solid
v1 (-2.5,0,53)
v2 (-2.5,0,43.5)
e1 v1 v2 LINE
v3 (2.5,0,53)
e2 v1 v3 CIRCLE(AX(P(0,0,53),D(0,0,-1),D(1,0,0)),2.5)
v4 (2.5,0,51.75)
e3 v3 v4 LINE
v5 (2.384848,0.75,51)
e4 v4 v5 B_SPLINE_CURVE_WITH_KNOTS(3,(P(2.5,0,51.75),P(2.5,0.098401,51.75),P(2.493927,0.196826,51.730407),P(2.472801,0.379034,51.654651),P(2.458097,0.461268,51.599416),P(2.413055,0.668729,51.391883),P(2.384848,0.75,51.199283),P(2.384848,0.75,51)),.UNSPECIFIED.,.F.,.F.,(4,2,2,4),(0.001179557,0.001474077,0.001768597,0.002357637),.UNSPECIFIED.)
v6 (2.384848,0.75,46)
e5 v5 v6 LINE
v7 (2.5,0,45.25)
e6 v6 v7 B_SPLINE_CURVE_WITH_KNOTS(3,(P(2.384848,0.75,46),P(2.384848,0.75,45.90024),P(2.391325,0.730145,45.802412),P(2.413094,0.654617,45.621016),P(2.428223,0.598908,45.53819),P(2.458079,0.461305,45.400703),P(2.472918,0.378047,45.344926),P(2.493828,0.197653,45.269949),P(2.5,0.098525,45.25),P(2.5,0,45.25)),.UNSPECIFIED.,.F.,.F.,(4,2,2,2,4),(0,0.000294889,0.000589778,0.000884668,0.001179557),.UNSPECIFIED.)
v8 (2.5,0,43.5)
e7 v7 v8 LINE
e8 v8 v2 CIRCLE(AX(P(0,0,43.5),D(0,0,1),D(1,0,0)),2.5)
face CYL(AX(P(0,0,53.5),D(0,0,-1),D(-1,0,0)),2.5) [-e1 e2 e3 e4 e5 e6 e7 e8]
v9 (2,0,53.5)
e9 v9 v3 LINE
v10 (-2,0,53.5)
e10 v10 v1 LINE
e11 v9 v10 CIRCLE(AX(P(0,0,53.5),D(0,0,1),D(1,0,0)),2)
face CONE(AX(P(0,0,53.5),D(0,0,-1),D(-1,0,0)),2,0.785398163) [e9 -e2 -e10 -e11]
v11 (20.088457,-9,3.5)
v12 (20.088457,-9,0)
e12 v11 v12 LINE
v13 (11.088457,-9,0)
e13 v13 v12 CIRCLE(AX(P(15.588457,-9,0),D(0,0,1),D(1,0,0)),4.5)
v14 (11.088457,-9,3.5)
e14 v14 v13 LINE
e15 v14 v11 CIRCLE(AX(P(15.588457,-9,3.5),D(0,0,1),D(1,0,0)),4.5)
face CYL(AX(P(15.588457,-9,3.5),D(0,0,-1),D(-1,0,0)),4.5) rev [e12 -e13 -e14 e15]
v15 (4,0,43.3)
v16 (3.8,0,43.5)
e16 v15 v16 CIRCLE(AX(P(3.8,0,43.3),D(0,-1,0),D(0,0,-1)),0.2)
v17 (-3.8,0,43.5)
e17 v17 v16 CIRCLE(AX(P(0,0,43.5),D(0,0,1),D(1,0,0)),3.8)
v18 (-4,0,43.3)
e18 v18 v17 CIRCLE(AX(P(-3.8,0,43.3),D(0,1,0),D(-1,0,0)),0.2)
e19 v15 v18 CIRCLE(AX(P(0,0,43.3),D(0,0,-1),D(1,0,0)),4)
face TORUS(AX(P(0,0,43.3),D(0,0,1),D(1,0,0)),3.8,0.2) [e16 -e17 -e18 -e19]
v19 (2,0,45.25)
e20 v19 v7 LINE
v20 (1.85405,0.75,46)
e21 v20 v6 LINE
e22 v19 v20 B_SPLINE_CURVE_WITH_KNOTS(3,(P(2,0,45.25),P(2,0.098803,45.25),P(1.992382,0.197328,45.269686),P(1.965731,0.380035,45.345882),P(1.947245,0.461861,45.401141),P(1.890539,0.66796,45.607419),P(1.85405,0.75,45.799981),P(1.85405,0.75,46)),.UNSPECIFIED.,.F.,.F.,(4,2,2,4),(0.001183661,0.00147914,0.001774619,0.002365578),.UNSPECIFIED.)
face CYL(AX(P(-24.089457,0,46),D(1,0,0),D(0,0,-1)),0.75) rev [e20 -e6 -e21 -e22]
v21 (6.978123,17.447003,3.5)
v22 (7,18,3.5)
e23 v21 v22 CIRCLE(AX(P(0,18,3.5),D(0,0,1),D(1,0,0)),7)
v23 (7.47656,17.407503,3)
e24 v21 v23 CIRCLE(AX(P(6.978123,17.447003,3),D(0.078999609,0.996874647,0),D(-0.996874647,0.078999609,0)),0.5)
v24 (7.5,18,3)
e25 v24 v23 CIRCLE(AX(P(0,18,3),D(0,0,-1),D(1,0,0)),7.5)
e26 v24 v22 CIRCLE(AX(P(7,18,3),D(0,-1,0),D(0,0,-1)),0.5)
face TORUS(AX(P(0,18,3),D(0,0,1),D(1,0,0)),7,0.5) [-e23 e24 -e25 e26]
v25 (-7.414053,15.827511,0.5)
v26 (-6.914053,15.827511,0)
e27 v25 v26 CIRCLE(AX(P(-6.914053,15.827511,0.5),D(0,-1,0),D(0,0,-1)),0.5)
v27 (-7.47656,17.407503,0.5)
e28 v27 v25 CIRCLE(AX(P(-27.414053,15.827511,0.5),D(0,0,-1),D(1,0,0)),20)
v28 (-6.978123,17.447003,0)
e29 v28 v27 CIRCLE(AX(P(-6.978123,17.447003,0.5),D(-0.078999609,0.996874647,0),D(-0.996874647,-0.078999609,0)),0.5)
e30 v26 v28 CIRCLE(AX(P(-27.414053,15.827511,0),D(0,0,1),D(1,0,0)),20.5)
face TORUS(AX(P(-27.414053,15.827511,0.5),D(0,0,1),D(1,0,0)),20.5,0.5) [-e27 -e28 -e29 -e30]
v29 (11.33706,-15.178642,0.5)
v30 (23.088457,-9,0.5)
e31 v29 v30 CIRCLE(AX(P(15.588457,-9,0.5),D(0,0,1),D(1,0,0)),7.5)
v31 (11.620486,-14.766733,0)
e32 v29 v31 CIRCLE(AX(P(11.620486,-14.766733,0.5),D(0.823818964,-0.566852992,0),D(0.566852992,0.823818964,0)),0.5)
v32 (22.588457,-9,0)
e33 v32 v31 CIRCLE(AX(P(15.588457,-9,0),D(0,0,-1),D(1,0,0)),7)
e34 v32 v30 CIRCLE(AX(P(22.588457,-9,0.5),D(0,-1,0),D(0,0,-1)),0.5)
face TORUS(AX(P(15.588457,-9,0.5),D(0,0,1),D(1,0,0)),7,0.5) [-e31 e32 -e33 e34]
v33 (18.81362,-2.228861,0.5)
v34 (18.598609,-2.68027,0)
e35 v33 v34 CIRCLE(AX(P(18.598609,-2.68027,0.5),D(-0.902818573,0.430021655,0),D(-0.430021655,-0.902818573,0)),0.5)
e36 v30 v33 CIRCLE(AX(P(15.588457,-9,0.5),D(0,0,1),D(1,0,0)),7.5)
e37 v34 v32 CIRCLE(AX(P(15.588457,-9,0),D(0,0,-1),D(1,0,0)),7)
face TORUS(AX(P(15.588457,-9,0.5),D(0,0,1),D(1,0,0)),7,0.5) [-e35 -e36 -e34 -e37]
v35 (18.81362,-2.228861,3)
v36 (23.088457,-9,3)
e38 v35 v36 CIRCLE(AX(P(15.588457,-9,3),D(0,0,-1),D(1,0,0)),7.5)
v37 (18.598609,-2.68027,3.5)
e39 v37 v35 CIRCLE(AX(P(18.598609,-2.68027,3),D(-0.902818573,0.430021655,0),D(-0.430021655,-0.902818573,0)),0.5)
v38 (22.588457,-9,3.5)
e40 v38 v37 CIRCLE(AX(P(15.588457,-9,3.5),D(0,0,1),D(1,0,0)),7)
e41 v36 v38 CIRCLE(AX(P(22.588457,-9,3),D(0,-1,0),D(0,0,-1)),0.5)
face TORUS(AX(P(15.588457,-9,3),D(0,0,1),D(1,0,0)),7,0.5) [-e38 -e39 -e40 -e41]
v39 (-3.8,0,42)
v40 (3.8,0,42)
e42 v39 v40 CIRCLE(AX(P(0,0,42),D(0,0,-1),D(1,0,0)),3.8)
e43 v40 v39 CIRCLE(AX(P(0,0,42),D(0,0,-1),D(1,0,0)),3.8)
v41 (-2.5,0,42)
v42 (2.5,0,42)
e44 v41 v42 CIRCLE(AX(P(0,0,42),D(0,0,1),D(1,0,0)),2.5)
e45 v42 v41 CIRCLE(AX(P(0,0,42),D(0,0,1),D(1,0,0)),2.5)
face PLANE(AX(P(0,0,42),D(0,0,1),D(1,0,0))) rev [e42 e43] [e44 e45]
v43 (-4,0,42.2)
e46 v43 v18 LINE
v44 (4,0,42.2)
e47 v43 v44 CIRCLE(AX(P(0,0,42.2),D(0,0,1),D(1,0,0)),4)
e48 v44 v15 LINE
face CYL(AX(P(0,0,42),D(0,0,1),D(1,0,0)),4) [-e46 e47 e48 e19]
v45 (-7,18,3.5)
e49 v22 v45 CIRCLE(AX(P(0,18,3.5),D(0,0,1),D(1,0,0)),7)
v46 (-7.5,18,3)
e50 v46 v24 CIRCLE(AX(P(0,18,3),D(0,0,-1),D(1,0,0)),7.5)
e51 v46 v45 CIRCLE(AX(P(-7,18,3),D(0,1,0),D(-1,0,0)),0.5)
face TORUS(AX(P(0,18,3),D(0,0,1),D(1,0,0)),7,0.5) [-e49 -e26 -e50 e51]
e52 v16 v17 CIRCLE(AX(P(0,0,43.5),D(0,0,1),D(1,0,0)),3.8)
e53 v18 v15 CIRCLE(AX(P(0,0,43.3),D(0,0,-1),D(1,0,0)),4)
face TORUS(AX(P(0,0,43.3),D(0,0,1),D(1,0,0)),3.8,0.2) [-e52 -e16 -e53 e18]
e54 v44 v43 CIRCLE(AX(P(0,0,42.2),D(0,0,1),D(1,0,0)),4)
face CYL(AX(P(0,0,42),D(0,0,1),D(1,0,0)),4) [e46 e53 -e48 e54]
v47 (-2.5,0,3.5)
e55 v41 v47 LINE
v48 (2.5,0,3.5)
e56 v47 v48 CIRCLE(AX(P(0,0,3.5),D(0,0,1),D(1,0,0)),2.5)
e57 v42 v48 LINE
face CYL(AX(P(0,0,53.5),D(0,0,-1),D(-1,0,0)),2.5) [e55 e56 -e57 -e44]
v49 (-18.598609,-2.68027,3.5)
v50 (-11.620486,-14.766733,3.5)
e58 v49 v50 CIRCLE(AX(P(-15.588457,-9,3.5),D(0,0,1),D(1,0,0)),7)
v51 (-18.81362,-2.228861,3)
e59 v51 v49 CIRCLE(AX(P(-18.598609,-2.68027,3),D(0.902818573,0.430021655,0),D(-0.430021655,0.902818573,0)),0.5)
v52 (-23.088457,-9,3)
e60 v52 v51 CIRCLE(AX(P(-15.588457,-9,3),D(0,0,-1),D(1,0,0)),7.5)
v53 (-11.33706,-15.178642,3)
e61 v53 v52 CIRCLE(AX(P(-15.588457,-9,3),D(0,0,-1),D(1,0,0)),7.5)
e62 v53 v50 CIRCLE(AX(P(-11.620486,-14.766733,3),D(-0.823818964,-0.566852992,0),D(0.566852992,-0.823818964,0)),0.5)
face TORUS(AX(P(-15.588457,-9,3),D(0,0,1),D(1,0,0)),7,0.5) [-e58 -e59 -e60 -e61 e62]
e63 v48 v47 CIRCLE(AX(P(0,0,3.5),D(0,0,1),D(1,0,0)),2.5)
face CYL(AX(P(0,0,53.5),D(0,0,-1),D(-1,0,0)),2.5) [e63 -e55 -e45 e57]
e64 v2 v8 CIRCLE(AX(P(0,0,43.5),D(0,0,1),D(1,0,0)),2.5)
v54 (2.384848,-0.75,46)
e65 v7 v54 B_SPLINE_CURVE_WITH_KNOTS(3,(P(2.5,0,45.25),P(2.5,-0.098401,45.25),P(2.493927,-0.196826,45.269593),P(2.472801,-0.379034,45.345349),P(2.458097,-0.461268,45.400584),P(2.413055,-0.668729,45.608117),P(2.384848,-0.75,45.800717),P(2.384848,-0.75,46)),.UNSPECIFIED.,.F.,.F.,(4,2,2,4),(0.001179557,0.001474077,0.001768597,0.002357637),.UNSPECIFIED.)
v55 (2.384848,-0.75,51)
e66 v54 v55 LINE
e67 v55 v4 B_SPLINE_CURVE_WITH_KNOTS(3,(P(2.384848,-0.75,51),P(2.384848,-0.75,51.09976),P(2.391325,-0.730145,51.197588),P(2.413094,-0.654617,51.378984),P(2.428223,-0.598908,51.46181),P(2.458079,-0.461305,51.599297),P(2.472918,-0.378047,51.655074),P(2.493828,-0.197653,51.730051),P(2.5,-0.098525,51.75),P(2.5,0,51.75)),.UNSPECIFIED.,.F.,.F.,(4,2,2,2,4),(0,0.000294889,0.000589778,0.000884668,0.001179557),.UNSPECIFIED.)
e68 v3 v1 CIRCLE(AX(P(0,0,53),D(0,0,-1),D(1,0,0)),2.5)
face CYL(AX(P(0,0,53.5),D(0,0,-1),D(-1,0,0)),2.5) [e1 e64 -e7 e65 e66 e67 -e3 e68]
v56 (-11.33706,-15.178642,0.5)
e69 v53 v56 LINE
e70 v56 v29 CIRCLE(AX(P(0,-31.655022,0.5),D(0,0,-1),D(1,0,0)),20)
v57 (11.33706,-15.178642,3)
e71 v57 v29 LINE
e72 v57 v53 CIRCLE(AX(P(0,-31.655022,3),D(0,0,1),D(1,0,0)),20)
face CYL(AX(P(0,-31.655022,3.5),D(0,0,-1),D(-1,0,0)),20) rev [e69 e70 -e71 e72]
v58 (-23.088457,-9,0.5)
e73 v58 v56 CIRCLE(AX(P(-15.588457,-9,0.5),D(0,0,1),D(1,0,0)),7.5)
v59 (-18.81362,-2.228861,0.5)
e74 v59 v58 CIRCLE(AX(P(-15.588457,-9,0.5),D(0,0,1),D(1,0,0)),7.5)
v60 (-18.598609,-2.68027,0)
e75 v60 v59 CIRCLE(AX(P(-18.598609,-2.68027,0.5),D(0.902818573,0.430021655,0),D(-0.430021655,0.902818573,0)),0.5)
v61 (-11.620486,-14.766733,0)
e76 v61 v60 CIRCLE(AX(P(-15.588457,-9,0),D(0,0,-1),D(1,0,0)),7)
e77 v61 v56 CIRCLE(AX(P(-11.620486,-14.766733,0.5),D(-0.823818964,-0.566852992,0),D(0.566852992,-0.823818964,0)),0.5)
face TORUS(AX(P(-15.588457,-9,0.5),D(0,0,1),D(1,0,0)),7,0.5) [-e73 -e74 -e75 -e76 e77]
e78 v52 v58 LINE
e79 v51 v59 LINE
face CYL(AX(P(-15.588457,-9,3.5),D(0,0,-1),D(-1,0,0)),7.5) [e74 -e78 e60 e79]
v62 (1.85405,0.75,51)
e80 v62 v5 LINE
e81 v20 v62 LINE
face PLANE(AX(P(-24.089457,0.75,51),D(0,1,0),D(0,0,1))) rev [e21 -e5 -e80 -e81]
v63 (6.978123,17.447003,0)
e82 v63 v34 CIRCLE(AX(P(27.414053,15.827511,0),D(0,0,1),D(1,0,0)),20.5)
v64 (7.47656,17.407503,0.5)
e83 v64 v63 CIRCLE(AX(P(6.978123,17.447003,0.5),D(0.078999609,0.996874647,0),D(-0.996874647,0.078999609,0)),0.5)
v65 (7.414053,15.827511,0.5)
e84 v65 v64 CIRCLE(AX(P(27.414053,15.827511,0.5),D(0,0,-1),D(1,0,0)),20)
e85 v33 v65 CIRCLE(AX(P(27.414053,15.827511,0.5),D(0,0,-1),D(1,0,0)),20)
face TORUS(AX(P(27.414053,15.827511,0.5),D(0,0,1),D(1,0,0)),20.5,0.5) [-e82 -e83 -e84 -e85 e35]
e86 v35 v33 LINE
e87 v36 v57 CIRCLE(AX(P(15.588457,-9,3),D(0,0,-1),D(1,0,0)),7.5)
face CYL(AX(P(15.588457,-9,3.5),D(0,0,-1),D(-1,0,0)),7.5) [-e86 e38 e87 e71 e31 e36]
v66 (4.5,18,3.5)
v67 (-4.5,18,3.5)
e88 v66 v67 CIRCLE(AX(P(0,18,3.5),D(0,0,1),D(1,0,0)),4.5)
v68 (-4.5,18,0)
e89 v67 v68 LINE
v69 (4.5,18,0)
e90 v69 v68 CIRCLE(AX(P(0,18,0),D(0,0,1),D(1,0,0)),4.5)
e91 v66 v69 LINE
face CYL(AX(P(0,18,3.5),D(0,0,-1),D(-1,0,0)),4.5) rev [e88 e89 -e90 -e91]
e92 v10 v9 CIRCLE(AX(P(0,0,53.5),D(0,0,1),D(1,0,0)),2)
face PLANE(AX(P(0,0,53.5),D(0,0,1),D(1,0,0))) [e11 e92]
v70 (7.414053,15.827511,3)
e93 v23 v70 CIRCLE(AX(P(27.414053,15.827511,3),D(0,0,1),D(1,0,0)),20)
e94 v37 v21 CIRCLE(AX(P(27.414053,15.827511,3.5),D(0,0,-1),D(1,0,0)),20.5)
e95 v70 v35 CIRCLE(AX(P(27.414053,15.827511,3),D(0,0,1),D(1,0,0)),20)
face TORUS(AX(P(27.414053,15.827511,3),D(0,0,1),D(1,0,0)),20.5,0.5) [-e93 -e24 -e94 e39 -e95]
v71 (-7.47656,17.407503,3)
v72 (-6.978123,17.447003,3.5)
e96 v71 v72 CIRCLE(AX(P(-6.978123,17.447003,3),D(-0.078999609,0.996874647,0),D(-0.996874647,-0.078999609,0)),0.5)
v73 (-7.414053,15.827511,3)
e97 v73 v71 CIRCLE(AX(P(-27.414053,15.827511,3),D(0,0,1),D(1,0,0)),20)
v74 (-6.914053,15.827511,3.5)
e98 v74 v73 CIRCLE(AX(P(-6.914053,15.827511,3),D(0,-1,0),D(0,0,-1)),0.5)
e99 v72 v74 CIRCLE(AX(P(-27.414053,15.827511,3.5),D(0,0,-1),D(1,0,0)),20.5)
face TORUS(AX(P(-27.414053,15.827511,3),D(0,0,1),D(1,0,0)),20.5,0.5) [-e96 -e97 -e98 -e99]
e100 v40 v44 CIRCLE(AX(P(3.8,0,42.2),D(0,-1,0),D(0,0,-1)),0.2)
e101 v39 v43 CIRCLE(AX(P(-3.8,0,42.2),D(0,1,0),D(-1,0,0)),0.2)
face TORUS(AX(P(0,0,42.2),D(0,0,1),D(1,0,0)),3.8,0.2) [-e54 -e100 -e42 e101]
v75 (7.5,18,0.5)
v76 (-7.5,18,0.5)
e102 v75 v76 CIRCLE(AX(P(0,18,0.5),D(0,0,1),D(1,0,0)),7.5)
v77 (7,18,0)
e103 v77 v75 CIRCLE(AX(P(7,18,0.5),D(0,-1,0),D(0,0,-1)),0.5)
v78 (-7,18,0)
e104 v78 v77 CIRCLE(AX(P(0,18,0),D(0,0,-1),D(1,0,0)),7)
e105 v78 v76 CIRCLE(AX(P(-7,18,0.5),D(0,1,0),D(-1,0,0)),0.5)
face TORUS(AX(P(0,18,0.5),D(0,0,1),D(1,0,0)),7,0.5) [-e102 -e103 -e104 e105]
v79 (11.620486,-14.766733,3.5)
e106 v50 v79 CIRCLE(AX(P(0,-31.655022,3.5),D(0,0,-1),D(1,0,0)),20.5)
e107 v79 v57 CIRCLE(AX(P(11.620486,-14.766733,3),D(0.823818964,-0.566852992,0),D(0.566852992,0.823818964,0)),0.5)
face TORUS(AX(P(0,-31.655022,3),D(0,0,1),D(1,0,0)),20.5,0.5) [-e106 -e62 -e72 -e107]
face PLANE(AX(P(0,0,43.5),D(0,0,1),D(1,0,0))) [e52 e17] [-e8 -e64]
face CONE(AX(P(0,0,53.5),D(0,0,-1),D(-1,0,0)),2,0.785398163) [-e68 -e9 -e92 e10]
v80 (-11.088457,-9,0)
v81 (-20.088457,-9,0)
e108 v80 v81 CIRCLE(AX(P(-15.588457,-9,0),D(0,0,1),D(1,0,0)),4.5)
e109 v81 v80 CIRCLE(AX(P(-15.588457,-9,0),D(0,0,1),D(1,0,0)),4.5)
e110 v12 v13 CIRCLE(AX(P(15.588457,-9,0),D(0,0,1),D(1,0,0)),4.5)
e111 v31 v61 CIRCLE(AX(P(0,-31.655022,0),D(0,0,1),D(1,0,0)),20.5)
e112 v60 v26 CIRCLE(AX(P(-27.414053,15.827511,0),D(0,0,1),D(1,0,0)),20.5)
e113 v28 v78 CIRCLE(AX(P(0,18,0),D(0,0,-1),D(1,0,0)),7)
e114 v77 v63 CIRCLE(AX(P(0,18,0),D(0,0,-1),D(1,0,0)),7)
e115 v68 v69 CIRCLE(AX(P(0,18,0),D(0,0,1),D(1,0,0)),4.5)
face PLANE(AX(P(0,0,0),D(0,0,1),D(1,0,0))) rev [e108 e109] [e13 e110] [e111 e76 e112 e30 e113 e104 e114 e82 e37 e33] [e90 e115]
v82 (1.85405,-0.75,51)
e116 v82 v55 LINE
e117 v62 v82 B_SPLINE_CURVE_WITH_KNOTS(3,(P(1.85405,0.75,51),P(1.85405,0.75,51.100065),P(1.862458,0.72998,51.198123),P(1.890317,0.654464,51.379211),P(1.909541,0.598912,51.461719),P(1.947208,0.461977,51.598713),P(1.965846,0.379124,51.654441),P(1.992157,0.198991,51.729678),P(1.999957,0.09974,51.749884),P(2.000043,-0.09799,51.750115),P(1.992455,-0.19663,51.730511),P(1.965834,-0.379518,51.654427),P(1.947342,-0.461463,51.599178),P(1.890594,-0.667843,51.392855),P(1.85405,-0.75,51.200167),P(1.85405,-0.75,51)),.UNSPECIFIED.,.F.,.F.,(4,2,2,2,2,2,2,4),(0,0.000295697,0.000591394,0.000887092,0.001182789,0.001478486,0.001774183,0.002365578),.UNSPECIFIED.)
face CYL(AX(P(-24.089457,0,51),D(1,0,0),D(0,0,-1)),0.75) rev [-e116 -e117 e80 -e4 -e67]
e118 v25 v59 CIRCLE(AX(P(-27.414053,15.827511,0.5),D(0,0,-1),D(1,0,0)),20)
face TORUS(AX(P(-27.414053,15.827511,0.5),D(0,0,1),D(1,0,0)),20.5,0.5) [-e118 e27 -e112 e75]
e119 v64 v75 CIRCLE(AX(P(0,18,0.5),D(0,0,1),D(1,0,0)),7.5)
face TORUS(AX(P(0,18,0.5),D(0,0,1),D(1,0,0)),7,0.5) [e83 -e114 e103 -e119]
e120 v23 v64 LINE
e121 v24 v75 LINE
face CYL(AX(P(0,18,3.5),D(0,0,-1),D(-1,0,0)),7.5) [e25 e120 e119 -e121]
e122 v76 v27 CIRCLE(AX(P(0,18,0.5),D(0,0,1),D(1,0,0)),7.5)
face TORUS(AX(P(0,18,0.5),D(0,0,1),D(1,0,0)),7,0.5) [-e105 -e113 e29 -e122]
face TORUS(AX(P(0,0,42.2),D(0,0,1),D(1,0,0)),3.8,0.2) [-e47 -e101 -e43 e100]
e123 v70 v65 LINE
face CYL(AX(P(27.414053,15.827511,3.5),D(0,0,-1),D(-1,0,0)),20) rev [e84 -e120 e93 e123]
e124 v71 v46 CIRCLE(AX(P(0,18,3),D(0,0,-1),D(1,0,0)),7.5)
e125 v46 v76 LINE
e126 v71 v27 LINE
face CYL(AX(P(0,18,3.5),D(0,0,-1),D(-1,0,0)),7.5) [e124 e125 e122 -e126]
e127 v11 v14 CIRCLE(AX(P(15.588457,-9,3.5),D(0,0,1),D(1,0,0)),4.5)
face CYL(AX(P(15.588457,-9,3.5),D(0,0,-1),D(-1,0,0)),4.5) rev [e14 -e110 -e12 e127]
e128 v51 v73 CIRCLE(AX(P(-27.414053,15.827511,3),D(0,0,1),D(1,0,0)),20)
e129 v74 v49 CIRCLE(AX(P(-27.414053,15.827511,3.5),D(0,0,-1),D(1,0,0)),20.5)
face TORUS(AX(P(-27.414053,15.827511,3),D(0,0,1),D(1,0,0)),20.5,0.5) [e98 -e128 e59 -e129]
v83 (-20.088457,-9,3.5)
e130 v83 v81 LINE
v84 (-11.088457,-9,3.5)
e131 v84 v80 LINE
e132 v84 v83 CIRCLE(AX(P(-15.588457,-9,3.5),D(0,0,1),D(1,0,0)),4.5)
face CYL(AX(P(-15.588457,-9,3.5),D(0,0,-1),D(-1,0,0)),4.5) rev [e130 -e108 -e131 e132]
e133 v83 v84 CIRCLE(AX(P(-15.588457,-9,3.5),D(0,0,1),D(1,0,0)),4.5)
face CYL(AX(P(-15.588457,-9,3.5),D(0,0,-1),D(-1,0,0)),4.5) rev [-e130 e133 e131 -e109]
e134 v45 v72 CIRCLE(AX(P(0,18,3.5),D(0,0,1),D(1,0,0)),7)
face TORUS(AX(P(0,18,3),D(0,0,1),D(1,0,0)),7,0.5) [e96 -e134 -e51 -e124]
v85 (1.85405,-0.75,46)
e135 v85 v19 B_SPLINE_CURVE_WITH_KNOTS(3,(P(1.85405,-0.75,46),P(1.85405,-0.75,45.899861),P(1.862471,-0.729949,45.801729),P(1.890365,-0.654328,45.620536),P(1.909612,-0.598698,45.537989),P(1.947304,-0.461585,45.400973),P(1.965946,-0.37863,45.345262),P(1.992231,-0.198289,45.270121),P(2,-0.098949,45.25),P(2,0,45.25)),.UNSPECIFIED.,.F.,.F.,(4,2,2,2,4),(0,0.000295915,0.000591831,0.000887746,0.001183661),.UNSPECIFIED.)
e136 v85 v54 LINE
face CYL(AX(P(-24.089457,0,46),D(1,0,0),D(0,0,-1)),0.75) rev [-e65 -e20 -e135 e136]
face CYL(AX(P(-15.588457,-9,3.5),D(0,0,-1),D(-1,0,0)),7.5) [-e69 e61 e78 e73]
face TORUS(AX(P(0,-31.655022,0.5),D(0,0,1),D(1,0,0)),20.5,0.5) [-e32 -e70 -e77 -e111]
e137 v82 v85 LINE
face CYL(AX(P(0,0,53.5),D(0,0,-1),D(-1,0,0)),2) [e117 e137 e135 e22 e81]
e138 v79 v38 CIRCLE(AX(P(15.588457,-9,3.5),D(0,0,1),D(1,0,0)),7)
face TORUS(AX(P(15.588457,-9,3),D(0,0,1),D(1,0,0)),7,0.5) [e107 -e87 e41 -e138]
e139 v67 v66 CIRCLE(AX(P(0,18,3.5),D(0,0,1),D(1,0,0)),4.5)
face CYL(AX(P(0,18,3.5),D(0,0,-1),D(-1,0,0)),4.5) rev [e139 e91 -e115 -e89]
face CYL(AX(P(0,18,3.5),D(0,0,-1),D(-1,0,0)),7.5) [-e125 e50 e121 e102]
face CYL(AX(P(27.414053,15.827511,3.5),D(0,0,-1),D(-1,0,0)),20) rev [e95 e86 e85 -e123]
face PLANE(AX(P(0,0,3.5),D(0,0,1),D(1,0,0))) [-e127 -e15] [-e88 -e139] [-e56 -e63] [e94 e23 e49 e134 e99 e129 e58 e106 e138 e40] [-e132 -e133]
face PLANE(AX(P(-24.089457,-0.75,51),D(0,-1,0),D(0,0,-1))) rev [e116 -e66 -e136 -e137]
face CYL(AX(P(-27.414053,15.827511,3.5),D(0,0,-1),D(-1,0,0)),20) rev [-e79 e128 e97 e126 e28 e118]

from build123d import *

# Parameters (mm, degrees)
CARRIER_PLATE_PROFILE_R   = 7.5
CARRIER_PLATE_PROFILE_R_2 = 4.5
CARRIER_PLATE_DEPTH       = 3.5
SHAFT_PROFILE_5_R         = 2.5
SHAFT_5X50_DEPTH          = 50
SHAFT_START               = -10
COLLAR_PROFILE_R          = 4
SHAFT_COLLAR_DEPTH        = 1.5
SHAFT_KEYSEAT_REACH       = 70.605
SHAFT_KEYSEAT_END_RADIUS  = 2
SHAFT_START_2             = 5
SHAFT_END_CHAMFER_SIZE    = 0.5
COLLAR_EDGE_FILLET_R      = 0.2
PLATE_EDGE_FILLET_R       = 0.5


with BuildPart() as part:
    # Carrier Plate Profile → Carrier Plate (new body)
    # profile 1 of 4: a face of its own
    with BuildSketch(Plane.XY):
        with Locations((15.588457268, -9)):
            Circle(CARRIER_PLATE_PROFILE_R)
        with Locations((15.588457268, -9)):
            Circle(CARRIER_PLATE_PROFILE_R_2, mode=Mode.SUBTRACT)
    # profile 2 of 4: a face of its own
    with BuildSketch(Plane.XY):
        with Locations((0, 18)):
            Circle(CARRIER_PLATE_PROFILE_R)
        with Locations((0, 18)):
            Circle(CARRIER_PLATE_PROFILE_R_2, mode=Mode.SUBTRACT)
    # profile 3 of 4: a face of its own
    with BuildSketch(Plane.XY):
        with Locations((-15.588457268, -9)):
            Circle(CARRIER_PLATE_PROFILE_R)
        with Locations((-15.588457268, -9)):
            Circle(CARRIER_PLATE_PROFILE_R_2, mode=Mode.SUBTRACT)
    # profile 4 of 4: a face of its own
    with BuildSketch(Plane.XY):
        with BuildLine():
            ThreePointArc((7.476559852, 17.407502934), (0, 10.5), (-7.476559852, 17.407502934))
            ThreePointArc((-7.476559852, 17.407502934), (-10.093544717, 5.827510759), (-18.813619684, -2.228860702))
            ThreePointArc((-18.813619684, -2.228860702), (-11.584628982, -2.658126534), (-8.088457268, -9))
            ThreePointArc((-8.088457268, -9), (-8.950103527, -12.490309386), (-11.337059831, -15.178642232))
            ThreePointArc((-11.337059831, -15.178642232), (0, -11.655021518), (11.337059831, -15.178642232))
            ThreePointArc((11.337059831, -15.178642232), (9.09326674, -5.25), (18.813619684, -2.228860702))
            ThreePointArc((18.813619684, -2.228860702), (10.093544717, 5.827510759), (7.476559852, 17.407502934))
        make_face()
    extrude(amount=CARRIER_PLATE_DEPTH)

    # Shaft Profile Ø5 → Shaft Ø5x50 (add)
    with BuildSketch(Plane.XY.offset(3.5)):
        Circle(SHAFT_PROFILE_5_R)
    extrude(amount=SHAFT_5X50_DEPTH)

    # Collar Profile → Shaft Collar (add)
    with BuildSketch(Plane.XY.offset(53.5).offset(SHAFT_START)):
        Circle(COLLAR_PROFILE_R)
    extrude(amount=-SHAFT_COLLAR_DEPTH)

    # Shaft Keyseat: up to this cylinder (the profile starts outside it)
    shaft_keyseat_end = Plane(origin=(0, 0, 48.5), z_dir=(0, 0, -1)) * Cylinder(SHAFT_KEYSEAT_END_RADIUS, 146.21, mode=Mode.PRIVATE)
    # Keyseat Profile → Shaft Keyseat (cut, up to the surface)
    with BuildSketch(Plane(origin=(0, 0, 0), x_dir=(0, 0, -1), z_dir=(1, 0, 0)).offset(SHAFT_START_2), mode=Mode.PRIVATE) as shaft_keyseat_sk1:
        with BuildLine():
            Line((-51, 0.75), (-46, 0.75))
            ThreePointArc((-46, 0.75), (-45.25, 0), (-46, -0.75))
            Line((-46, -0.75), (-51, -0.75))
            ThreePointArc((-51, -0.75), (-51.75, 0), (-51, 0.75))
        make_face()
    shaft_keyseat_tool1 = extrude(shaft_keyseat_sk1.sketch, amount=-SHAFT_KEYSEAT_REACH, mode=Mode.PRIVATE) - shaft_keyseat_end
    add(shaft_keyseat_tool1.solids().sort_by_distance((5, 0, 48.5))[0], mode=Mode.SUBTRACT)

    # Shaft End Chamfer
    shaft_end_chamfer_edges = [part.edges().sort_by_distance(p)[0] for p in [
        (-2.5, 0, 53.5),
    ]]
    chamfer(shaft_end_chamfer_edges, length=SHAFT_END_CHAMFER_SIZE)

    # Collar Edge Fillet
    collar_edge_fillet_edges = [part.edges().sort_by_distance(p)[0] for p in [
        (-4, 0, 42),
        (-4, 0, 43.5),
    ]]
    fillet(collar_edge_fillet_edges, radius=COLLAR_EDGE_FILLET_R)

    # Plate Edge Fillet
    plate_edge_fillet_edges = [part.edges().sort_by_distance(p)[0] for p in [
        (0, -11.655021518, 0),
        (-22.083647797, -12.75, 0),
        (22.083647797, -12.75, 3.5),
        (-10.093544717, 5.827510759, 0),
        (0, 25.5, 0),
        (10.093544717, 5.827510759, 0),
        (22.083647797, -12.75, 0),
        (10.093544717, 5.827510759, 3.5),
        (0, 25.5, 3.5),
        (-10.093544717, 5.827510759, 3.5),
        (-22.083647797, -12.75, 3.5),
        (0, -11.655021518, 3.5),
    ]]
    fillet(plate_edge_fillet_edges, radius=PLATE_EDGE_FILLET_R)


solid = part.part
